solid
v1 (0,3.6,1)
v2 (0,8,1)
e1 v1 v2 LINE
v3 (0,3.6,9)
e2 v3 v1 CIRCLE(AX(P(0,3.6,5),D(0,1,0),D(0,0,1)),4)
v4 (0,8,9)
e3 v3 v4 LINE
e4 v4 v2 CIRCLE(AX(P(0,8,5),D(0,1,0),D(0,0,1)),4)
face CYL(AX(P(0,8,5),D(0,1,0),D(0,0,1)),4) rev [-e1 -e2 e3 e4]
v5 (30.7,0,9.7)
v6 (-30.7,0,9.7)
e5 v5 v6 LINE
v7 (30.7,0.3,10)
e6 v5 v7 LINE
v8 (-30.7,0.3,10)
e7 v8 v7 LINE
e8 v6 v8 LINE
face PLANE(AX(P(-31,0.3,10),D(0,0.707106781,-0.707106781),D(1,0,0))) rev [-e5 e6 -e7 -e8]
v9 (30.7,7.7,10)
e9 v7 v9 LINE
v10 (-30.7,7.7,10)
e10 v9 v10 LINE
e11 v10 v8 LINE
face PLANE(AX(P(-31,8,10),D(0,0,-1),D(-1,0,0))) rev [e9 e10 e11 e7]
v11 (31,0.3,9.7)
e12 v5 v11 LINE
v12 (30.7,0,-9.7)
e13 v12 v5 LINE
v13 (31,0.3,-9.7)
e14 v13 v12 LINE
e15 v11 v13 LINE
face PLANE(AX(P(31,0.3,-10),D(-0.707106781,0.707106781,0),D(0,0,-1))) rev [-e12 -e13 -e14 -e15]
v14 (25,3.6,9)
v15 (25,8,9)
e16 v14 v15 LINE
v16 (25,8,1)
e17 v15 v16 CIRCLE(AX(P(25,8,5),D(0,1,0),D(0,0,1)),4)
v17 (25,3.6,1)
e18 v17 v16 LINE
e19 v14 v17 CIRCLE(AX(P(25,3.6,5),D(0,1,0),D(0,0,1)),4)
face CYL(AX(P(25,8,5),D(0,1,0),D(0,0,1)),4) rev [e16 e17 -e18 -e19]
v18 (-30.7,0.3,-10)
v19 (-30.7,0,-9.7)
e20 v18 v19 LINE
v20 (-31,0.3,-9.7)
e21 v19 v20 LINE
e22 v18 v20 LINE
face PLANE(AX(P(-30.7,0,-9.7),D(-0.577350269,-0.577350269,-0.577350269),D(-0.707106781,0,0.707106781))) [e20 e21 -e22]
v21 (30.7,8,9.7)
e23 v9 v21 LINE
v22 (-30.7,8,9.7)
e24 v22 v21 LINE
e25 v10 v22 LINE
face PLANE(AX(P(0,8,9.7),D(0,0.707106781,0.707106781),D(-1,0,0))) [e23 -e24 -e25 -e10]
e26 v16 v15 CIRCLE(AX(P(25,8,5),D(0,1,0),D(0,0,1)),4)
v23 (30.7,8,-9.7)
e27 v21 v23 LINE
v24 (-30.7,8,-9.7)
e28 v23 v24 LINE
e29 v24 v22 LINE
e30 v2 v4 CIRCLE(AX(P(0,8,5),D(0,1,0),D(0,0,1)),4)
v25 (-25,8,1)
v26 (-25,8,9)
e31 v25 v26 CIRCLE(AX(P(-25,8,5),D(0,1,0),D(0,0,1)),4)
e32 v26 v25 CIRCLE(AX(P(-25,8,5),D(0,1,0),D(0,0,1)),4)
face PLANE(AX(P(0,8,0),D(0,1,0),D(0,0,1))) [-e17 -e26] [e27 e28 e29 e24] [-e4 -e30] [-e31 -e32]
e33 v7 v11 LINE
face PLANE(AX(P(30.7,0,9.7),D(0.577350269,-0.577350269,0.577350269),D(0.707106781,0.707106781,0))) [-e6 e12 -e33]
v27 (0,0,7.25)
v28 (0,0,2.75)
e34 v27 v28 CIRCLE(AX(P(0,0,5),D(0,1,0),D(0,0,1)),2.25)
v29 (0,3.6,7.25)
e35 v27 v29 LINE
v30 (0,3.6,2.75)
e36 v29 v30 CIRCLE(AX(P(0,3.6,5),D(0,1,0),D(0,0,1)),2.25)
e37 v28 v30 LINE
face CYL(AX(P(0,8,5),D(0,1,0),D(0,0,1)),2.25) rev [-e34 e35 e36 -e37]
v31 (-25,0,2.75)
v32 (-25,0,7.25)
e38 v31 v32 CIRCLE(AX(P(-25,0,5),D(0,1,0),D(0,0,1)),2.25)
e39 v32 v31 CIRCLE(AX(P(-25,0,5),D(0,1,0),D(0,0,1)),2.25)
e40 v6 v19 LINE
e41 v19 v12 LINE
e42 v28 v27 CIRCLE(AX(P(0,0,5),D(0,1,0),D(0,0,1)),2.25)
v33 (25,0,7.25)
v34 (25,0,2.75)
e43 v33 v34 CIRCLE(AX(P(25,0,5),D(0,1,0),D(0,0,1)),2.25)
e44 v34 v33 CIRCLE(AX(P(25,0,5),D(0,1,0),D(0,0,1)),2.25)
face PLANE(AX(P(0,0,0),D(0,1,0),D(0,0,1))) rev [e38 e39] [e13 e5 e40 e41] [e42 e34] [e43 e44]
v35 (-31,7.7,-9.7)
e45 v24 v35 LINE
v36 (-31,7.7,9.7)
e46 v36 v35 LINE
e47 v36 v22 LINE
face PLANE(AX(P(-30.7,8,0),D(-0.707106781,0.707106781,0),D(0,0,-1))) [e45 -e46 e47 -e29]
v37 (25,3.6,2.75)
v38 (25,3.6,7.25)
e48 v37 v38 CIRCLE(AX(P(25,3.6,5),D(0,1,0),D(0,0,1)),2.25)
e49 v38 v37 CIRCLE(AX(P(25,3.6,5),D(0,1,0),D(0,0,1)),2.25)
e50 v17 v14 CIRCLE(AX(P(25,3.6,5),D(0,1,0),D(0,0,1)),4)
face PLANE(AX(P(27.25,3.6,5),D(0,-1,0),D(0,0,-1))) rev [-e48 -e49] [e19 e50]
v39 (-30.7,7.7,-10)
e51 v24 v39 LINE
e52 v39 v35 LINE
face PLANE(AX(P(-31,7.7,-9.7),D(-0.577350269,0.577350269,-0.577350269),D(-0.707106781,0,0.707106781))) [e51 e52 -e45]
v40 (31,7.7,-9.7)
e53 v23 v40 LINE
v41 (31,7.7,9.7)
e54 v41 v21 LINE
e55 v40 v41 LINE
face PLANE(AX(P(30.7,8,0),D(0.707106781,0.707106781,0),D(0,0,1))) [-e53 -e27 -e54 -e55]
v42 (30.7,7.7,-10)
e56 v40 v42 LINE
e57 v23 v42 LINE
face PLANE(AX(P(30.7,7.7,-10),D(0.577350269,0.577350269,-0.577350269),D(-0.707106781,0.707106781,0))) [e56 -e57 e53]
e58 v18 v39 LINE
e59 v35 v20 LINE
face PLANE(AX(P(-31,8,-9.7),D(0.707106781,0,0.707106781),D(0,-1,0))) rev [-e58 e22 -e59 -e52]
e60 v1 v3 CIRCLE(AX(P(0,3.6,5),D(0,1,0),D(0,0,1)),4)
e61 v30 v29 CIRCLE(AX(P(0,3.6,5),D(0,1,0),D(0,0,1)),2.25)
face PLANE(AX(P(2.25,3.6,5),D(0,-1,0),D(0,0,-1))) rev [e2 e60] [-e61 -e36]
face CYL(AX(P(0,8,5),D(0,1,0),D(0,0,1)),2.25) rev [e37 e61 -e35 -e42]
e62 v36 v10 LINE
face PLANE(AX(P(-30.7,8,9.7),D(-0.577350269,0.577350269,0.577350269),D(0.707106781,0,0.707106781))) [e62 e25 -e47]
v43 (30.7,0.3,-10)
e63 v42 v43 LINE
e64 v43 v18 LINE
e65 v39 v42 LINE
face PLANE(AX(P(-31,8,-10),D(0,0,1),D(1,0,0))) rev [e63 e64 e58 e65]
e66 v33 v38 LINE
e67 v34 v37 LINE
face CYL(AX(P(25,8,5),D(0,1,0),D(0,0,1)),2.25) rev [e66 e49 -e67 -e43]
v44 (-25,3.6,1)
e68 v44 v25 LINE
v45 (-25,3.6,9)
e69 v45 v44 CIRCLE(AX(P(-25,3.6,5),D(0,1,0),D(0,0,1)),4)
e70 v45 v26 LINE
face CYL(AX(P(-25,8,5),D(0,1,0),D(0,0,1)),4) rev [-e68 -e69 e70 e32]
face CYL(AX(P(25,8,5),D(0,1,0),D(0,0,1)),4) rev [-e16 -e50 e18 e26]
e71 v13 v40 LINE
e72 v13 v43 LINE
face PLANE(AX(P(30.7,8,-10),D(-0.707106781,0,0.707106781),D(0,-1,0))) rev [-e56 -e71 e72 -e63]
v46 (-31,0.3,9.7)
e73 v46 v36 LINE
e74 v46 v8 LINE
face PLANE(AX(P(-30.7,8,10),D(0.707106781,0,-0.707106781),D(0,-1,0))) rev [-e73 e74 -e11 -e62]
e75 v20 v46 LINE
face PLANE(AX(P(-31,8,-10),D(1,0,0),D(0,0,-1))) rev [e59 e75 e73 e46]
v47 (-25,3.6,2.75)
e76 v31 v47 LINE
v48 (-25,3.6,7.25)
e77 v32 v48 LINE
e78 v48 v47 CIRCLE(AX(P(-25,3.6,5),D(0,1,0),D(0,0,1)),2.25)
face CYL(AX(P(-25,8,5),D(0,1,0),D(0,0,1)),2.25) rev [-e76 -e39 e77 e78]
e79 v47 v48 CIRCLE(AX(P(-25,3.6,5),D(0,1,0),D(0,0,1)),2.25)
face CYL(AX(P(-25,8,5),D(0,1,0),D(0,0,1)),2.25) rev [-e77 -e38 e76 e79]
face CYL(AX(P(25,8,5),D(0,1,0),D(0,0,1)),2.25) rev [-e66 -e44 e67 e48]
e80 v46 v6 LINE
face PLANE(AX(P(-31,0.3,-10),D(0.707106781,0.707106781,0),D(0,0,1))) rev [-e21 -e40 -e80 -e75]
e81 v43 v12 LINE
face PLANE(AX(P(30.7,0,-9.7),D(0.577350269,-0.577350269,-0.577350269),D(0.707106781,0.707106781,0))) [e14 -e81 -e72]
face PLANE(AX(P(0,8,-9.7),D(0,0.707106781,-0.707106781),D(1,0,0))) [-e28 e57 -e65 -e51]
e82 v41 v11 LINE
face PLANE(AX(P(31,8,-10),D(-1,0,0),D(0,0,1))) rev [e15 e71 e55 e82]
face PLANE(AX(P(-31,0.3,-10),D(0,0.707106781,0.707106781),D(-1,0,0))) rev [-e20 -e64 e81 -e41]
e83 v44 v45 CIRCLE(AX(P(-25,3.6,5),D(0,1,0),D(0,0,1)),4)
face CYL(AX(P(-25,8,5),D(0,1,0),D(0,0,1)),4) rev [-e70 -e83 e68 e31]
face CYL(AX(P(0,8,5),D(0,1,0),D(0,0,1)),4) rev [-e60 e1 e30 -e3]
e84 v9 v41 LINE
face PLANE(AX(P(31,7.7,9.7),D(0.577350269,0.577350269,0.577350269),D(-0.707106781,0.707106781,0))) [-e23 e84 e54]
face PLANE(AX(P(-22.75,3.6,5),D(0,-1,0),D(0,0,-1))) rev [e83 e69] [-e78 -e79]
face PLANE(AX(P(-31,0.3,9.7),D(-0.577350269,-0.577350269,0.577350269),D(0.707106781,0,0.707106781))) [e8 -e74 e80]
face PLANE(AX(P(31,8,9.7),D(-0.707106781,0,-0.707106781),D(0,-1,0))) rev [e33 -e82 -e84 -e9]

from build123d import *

# Parameters (mm, degrees)
SKETCH_1_W                   = 62
SKETCH_1_H                   = 20
EXTRUDE_1_DEPTH              = 8
HOLE_WIZARD_M4_1_D           = 4.5
HOLE_WIZARD_M4_1_CBORE_D     = 8
HOLE_WIZARD_M4_1_CBORE_DEPTH = 4.4
CHAMFER_1_SIZE               = 0.3


with BuildPart() as part:
    # 草图1 → 凸台-拉伸1 (new body)
    with BuildSketch(Plane(origin=(0, 0, 0), x_dir=(1, 0, 0), z_dir=(0, 1, 0))):
        Rectangle(SKETCH_1_W, SKETCH_1_H)
    extrude(amount=EXTRUDE_1_DEPTH)

    # M4 六角凹头螺钉的柱形沉头孔1 (through all)
    with Locations(Plane(origin=(0, 8, 0), x_dir=(1, 0, 0), z_dir=(0, 1, 0))):
        with Locations((-25, -5), (0, -5), (25, -5)):
            CounterBoreHole(HOLE_WIZARD_M4_1_D / 2, HOLE_WIZARD_M4_1_CBORE_D / 2, HOLE_WIZARD_M4_1_CBORE_DEPTH)

    # 倒角1
    chamfer_1_edges = [part.edges().sort_by_distance(p)[0] for p in [
        (-31, 8, 0),
        (0, 8, 10),
        (31, 8, 0),
        (0, 0, 10),
        (-31, 0, 0),
        (0, 0, -10),
        (31, 0, 0),
        (0, 8, -10),
        (31, 4, 10),
        (-31, 4, 10),
        (-31, 4, -10),
        (31, 4, -10),
    ]]
    chamfer(chamfer_1_edges, length=CHAMFER_1_SIZE)


solid = part.part
